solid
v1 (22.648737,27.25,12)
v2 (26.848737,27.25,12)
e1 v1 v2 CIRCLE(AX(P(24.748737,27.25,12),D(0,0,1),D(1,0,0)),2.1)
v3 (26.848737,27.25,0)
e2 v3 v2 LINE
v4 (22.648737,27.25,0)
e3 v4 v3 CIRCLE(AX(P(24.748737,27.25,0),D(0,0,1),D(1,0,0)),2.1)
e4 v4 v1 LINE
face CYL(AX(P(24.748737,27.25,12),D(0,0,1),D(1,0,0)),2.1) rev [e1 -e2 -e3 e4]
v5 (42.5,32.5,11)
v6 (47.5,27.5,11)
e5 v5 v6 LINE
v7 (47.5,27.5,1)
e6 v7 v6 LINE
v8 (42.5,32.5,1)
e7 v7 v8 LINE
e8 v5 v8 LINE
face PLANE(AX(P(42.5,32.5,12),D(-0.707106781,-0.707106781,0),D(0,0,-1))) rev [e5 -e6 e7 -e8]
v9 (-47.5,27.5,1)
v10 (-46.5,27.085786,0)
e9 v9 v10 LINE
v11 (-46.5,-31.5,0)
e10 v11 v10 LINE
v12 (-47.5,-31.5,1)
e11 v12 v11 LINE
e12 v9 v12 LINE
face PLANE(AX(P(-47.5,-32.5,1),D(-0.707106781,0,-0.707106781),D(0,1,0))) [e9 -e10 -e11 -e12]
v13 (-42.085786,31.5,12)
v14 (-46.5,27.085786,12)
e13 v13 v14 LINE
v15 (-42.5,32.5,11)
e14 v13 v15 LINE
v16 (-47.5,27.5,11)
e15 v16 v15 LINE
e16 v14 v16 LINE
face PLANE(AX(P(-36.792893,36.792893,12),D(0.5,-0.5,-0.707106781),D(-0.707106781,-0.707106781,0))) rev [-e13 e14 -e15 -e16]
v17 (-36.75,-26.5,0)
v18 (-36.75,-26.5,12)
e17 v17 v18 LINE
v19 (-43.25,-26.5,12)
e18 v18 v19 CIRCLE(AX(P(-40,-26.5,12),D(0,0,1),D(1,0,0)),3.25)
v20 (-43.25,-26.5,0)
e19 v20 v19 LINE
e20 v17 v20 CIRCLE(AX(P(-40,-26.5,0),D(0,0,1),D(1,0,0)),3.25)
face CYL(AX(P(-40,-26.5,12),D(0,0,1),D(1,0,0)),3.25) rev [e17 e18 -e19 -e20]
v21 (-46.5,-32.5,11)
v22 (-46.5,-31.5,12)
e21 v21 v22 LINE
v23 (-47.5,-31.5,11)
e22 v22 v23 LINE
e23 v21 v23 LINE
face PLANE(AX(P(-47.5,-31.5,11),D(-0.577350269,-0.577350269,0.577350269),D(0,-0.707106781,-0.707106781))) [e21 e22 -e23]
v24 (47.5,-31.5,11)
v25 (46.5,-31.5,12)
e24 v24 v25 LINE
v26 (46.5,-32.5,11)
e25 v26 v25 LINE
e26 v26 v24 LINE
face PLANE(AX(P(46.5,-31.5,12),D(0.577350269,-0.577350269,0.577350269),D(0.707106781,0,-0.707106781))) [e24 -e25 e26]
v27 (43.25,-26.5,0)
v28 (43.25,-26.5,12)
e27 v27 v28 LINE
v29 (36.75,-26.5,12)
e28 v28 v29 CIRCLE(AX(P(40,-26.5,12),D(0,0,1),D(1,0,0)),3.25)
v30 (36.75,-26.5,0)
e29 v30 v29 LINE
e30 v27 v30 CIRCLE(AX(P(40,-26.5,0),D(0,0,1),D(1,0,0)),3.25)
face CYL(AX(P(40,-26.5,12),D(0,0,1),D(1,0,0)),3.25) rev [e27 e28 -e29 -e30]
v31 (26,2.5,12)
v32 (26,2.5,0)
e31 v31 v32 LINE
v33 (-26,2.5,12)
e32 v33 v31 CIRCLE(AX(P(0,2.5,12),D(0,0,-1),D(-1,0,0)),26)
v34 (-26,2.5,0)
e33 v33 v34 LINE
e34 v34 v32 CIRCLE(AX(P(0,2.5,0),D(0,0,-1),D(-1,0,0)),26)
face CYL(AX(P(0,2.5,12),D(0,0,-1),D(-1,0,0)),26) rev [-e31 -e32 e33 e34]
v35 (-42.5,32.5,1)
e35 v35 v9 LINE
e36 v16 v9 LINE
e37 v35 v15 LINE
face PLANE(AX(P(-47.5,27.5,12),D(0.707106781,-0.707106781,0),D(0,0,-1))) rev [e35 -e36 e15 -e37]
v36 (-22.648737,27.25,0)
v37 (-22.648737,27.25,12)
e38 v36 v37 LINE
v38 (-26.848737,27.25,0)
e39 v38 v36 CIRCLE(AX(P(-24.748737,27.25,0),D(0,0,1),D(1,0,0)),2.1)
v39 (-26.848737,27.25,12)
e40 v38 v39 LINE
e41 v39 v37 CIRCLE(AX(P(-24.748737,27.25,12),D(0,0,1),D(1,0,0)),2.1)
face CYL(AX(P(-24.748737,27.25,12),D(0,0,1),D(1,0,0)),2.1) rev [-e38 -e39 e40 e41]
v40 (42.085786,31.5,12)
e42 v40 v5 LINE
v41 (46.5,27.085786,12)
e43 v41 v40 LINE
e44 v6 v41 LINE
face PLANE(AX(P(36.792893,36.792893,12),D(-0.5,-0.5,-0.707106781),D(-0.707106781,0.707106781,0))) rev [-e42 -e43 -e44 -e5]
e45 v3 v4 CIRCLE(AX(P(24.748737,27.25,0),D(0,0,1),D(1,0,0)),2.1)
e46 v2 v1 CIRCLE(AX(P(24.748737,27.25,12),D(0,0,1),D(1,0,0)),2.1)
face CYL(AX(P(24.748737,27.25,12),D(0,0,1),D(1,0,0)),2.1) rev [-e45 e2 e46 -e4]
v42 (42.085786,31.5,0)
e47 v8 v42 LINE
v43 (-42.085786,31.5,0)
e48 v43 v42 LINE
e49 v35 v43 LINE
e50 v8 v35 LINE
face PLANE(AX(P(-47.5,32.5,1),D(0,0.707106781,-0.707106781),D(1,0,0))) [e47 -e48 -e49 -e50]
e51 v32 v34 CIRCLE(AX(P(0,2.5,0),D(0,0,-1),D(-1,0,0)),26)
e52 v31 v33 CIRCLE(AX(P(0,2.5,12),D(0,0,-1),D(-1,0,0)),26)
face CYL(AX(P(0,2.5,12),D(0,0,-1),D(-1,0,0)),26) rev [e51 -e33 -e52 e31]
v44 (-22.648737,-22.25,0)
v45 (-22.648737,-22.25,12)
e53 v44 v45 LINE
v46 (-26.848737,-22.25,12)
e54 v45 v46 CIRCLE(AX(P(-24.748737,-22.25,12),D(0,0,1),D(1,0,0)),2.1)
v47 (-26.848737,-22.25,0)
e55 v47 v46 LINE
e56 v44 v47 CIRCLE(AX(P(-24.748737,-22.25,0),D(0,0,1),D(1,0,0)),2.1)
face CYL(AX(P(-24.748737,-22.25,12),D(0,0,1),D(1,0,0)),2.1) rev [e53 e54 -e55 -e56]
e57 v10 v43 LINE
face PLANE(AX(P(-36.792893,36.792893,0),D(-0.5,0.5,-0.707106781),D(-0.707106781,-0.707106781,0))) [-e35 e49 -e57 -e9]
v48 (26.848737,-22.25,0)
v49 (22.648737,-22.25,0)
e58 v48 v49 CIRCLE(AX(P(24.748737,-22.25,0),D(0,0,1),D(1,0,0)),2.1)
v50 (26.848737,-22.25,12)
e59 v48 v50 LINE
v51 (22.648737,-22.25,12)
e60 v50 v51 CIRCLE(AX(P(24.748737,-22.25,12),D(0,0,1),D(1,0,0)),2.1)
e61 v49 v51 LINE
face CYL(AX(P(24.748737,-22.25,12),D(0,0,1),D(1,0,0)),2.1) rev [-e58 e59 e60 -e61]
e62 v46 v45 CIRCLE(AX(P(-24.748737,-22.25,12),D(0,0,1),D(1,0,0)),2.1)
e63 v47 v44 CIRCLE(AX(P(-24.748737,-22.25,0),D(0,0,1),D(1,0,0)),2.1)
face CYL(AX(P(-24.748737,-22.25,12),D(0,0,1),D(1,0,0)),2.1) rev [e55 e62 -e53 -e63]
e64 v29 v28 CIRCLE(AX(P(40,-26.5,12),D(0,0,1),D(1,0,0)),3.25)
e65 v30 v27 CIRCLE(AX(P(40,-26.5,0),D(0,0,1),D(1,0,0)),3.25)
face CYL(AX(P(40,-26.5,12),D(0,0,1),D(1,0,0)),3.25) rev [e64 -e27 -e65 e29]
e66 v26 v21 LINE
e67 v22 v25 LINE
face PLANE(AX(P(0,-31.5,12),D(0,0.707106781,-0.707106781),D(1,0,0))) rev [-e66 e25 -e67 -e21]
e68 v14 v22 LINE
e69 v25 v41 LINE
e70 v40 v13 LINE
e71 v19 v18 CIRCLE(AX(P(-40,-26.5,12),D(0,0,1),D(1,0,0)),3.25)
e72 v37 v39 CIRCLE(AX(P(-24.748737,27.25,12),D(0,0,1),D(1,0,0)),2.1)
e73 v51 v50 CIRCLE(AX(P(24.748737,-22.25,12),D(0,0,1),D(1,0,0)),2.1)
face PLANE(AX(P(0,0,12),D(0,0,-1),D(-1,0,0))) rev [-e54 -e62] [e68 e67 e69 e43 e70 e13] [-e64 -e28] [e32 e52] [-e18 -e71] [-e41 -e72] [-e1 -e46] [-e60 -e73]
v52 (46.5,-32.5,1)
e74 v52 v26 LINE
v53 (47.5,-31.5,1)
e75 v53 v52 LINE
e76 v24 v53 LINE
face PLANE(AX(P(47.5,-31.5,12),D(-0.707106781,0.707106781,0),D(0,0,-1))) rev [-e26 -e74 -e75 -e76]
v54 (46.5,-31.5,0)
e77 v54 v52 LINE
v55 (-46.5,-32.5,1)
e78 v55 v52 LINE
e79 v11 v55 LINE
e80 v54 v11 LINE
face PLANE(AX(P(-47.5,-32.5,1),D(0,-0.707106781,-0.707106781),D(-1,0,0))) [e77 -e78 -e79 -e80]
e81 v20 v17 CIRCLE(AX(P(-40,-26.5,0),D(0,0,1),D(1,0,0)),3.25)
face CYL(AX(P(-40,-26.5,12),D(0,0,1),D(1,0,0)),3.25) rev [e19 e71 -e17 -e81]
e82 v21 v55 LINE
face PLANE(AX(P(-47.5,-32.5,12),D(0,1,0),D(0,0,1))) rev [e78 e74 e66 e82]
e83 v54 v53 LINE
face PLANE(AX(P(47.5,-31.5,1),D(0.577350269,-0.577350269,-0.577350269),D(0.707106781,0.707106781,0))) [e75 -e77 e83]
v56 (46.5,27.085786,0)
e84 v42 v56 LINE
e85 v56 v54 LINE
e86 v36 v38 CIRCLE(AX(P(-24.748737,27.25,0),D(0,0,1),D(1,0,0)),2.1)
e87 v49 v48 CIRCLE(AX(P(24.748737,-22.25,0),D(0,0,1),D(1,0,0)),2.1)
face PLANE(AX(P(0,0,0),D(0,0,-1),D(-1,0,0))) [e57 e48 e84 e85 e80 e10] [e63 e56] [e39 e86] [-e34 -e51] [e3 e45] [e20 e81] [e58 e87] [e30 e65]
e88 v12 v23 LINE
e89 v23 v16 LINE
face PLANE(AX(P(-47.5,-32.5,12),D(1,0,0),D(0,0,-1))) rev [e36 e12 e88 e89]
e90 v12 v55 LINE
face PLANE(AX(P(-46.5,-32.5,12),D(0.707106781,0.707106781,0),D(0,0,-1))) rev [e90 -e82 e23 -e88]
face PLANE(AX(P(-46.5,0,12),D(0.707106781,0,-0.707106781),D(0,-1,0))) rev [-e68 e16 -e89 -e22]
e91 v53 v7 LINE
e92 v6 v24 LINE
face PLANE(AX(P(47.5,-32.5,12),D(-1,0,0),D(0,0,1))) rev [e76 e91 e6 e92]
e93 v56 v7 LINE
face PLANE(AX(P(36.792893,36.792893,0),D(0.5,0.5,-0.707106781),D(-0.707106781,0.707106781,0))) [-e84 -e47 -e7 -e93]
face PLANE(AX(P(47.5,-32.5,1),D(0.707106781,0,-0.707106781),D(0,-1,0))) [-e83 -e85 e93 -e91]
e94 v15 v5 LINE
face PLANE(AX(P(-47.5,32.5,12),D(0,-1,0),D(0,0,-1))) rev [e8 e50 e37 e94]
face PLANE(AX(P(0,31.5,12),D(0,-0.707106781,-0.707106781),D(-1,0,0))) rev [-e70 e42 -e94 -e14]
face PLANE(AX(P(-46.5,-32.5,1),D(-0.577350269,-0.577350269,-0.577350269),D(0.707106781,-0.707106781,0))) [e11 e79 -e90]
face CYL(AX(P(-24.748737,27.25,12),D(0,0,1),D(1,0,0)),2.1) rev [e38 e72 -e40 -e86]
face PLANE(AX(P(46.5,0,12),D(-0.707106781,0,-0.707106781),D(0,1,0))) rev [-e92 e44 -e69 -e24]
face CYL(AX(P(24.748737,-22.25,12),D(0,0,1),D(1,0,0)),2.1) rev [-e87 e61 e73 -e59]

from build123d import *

# Parameters (mm, degrees)
SKETCH_1_W              = 95
SKETCH_1_H              = 65
EXTRUDE_1_DEPTH         = 12
HOLE_WIZARD_6_5_6_5_1_D = 6.5
CHAMFER_1_SIZE          = 5
SKETCH_4_R              = 26
CUT_EXTRUDE_1_DEPTH     = 59.792006259
HOLE_WIZARD_M5_1_D      = 4.2
CHAMFER_2_SIZE          = 1


with BuildPart() as part:
    # 草图1 → 凸台-拉伸1 (new body)
    with BuildSketch(Plane.XY):
        Rectangle(SKETCH_1_W, SKETCH_1_H)
    extrude(amount=EXTRUDE_1_DEPTH)

    # Ø6.5 (6.5) 直径孔1 (through all)
    with Locations(Plane.XY.offset(12)):
        with Locations((-40, -26.5), (40, -26.5)):
            Hole(HOLE_WIZARD_6_5_6_5_1_D / 2)

    # 倒角1
    chamfer_1_edges = [part.edges().sort_by_distance(p)[0] for p in [
        (-47.5, 32.5, 6),
        (47.5, 32.5, 6),
    ]]
    chamfer(chamfer_1_edges, length=CHAMFER_1_SIZE)

    # 草图4 → 切除-拉伸1 (cut, through all)
    with BuildSketch(Plane(origin=(0, 0, 0), x_dir=(-1, 0, 0), z_dir=(0, 0, -1))):
        with Locations((0, 2.5)):
            Circle(SKETCH_4_R)
    extrude(amount=-CUT_EXTRUDE_1_DEPTH, mode=Mode.SUBTRACT)

    # M5 螺纹孔1 (through all)
    with Locations(Plane.XY.offset(12)):
        with Locations((-24.748737342, 27.25), (24.748737342, 27.25), (24.748737342, -22.25), (-24.748737342, -22.25)):
            Hole(HOLE_WIZARD_M5_1_D / 2)

    # 倒角2
    chamfer_2_edges = [part.edges().sort_by_distance(p)[0] for p in [
        (0, -32.5, 12),
        (0, 32.5, 0),
        (0, 32.5, 12),
        (-47.5, -2.5, 0),
        (-45, 30, 0),
        (45, 30, 0),
        (-47.5, -2.5, 12),
        (-45, 30, 12),
        (45, 30, 12),
        (47.5, -2.5, 12),
        (0, -32.5, 0),
        (47.5, -2.5, 0),
        (47.5, -32.5, 6),
        (-47.5, -32.5, 6),
    ]]
    chamfer(chamfer_2_edges, length=CHAMFER_2_SIZE)


solid = part.part
